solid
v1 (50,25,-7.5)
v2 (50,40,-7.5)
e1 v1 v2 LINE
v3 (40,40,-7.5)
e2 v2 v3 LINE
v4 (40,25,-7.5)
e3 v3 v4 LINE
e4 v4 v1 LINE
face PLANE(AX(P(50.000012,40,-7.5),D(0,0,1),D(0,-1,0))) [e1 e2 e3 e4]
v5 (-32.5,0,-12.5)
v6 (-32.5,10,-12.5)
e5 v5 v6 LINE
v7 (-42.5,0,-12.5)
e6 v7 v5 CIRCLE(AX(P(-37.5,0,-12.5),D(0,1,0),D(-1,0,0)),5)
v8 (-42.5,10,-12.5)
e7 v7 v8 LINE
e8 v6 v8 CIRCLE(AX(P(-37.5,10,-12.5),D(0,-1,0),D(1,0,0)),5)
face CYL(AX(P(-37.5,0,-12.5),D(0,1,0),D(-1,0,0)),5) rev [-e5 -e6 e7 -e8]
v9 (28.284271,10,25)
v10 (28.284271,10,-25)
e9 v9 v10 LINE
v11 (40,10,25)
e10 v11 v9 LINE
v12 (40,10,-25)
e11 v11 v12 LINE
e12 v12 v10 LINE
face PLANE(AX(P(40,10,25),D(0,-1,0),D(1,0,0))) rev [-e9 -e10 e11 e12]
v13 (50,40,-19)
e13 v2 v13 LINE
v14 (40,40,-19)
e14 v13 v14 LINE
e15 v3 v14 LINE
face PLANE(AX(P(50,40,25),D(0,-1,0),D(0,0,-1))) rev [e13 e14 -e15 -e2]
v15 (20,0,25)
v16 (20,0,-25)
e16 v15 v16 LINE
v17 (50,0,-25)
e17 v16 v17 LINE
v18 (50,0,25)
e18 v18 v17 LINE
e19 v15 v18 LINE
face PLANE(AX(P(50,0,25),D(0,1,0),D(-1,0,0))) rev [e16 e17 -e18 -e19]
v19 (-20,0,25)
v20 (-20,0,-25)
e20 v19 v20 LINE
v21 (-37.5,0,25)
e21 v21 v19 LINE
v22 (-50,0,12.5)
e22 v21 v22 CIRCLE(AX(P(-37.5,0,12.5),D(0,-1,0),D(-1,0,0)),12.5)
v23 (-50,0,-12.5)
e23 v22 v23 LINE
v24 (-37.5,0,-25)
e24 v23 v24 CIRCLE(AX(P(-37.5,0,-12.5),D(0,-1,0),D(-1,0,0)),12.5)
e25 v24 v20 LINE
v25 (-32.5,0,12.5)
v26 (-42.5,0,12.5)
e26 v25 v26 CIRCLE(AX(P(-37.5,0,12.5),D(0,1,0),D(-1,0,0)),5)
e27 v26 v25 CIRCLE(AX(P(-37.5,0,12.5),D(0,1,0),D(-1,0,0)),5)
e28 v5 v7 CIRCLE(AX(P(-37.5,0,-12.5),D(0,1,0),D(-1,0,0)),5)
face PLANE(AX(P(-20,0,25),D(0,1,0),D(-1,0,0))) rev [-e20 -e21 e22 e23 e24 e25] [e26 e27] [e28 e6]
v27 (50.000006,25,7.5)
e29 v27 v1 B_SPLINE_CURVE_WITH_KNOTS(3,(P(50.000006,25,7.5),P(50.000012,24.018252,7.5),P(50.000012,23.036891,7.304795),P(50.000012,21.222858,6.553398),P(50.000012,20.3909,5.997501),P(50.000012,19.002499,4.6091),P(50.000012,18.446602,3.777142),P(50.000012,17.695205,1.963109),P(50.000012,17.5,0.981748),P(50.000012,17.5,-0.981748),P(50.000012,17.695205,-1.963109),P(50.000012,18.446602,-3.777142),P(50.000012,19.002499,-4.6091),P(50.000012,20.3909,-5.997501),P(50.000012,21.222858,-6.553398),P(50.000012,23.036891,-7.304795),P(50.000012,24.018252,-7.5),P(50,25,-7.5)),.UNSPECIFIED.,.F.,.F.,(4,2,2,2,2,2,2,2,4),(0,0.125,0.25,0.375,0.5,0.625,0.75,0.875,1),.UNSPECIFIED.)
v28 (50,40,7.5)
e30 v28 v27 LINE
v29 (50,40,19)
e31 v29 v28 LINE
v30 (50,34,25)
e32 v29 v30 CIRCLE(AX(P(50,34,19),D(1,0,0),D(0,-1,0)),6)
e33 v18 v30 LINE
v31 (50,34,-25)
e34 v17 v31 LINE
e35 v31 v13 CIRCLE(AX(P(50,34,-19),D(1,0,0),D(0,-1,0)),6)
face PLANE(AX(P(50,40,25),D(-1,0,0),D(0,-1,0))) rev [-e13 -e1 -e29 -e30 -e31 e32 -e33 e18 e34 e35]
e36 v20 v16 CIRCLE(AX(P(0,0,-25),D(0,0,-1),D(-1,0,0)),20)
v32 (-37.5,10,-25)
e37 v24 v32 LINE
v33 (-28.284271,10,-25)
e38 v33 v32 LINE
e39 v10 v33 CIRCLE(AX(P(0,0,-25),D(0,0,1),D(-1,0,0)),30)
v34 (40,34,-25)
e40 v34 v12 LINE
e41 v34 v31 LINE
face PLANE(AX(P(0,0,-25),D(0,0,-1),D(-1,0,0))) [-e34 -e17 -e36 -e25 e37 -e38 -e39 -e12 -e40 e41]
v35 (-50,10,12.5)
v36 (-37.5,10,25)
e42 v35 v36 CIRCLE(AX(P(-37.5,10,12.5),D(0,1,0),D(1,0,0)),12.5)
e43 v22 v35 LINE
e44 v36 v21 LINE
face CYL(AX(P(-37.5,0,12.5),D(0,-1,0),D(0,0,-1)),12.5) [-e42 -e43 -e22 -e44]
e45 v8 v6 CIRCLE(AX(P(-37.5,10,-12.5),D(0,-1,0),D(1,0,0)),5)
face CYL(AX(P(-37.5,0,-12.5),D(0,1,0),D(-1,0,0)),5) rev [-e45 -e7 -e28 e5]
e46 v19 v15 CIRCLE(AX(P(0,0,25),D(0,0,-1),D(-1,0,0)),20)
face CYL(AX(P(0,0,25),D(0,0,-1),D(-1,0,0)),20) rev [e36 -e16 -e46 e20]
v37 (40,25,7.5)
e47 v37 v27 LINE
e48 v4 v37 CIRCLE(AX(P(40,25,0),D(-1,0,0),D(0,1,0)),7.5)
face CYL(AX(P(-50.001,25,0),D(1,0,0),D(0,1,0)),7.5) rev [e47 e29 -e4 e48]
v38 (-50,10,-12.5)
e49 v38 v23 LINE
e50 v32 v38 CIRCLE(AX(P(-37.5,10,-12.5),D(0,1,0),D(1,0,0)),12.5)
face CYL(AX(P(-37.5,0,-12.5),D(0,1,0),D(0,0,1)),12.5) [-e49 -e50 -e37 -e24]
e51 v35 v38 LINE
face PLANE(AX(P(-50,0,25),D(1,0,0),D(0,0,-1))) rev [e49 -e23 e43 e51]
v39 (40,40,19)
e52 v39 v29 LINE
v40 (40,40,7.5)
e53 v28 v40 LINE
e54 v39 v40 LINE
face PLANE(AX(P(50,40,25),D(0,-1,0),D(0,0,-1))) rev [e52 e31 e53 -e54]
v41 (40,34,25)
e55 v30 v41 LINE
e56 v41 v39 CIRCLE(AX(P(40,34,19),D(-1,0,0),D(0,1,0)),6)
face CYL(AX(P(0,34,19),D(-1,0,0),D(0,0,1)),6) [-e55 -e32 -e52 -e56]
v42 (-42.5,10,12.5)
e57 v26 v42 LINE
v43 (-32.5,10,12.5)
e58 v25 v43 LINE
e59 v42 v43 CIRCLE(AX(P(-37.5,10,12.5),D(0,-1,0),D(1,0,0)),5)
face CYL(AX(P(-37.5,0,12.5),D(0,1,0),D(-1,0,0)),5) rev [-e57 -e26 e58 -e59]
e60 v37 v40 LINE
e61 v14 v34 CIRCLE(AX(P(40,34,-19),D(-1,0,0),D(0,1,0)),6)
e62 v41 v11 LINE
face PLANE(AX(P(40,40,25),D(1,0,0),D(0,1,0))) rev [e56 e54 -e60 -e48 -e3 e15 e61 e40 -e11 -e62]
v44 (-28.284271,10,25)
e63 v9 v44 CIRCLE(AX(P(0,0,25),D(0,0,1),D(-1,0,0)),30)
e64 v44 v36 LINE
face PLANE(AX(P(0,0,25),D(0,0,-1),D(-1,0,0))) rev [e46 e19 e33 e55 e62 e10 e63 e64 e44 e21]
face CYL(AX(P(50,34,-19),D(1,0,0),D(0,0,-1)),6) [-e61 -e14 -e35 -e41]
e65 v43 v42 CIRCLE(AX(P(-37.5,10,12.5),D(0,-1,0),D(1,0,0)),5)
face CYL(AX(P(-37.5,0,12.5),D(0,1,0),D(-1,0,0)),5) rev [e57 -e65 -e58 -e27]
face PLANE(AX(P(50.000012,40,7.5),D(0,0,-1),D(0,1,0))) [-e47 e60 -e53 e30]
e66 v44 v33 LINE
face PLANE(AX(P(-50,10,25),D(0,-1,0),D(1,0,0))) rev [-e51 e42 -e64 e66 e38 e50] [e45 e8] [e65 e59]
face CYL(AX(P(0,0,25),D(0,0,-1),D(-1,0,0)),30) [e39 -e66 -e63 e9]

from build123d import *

# Parameters (mm, degrees)
BASE_BODY_EXTRUDE_DEPTH         = 25
FLANGE_END_ROUNDS_R12_5_R       = 12.5
EDGE_FILLETS_R6_R               = 6
FLANGE_BOLT_HOLES_2X_DEPTH      = 64.442887702
FLANGE_BOLT_HOLES_2X_DEPTH_BACK = 64.442887702
FLANGE_HOLES_SKETCH_R           = 5
FORK_SLOT_REACH                 = 112.567
FORK_SLOT_DIRECTION_2_DEPTH     = 111.566721937


with BuildPart() as part:
    # Base Profile Sketch → Base Body Extrude (new, symmetric)
    with BuildSketch(Plane.XY):
        with BuildLine():
            Line((50, 40), (50, 0))
            Line((50, 0), (20, 0))
            ThreePointArc((20, 0), (0, 20), (-20, 0))
            Line((-20, 0), (-50, 0))
            Line((-50, 0), (-50, 10))
            Line((-50, 10), (-28.284271247, 10))
            ThreePointArc((-28.284271247, 10), (0, 30), (28.284271247, 10))
            Line((28.284271247, 10), (40, 10))
            Line((40, 10), (40, 40))
            Line((40, 40), (50, 40))
        make_face()
    extrude(amount=BASE_BODY_EXTRUDE_DEPTH, both=True)

    # Flange End Rounds R12.5
    flange_end_rounds_r12_5_edges = [part.edges().sort_by_distance(p)[0] for p in [
        (-50, 5, 25),
        (-50, 5, -25),
    ]]
    fillet(flange_end_rounds_r12_5_edges, radius=FLANGE_END_ROUNDS_R12_5_R)

    # Edge Fillets R6
    edge_fillets_r6_edges = [part.edges().sort_by_distance(p)[0] for p in [
        (45, 40, -25),
        (45, 40, 25),
    ]]
    fillet(edge_fillets_r6_edges, radius=EDGE_FILLETS_R6_R)

    # Flange Holes Sketch → Flange Bolt Holes 2x (cut, two sides: drawn at the far end of the back side and taken through both)
    with BuildSketch(Plane(origin=(0, 10, 0), x_dir=(1, 0, 0), z_dir=(0, 1, 0)).offset(-FLANGE_BOLT_HOLES_2X_DEPTH_BACK)):
        with Locations(Location((-37.5, -12.5, 0), (0, 0, 180))):
            Circle(FLANGE_HOLES_SKETCH_R)
        with Locations(Location((-37.5, 12.5, 0), (0, 0, 180))):
            Circle(FLANGE_HOLES_SKETCH_R)
    extrude(amount=FLANGE_BOLT_HOLES_2X_DEPTH + FLANGE_BOLT_HOLES_2X_DEPTH_BACK, mode=Mode.SUBTRACT)

    # Fork Slot Sketch → Fork Slot (cut, up to next)
    with BuildSketch(Plane(origin=(50, 0, 0), x_dir=(0, 0, -1), z_dir=(1, 0, 0)), mode=Mode.PRIVATE) as fork_slot_sk1:
        with BuildLine():
            Line((7.5, 40), (7.5, 25))
            ThreePointArc((7.5, 25), (0, 17.5), (-7.5, 25))
            Line((-7.5, 25), (-7.5, 40))
            Line((-7.5, 40), (7.5, 40))
        make_face()
    fork_slot_tool1 = extrude(fork_slot_sk1.sketch, amount=-FORK_SLOT_REACH, mode=Mode.PRIVATE) & part.part
    add(fork_slot_tool1.solids().sort_by_distance((50, 29.487689, 0))[0], mode=Mode.SUBTRACT)

    # Fork Slot Sketch → Fork Slot direction 2 (cut)
    with BuildSketch(Plane(origin=(50, 0, 0), x_dir=(0, 0, -1), z_dir=(1, 0, 0))):
        with BuildLine():
            Line((7.5, 40), (7.5, 25))
            ThreePointArc((7.5, 25), (0, 17.5), (-7.5, 25))
            Line((-7.5, 25), (-7.5, 40))
            Line((-7.5, 40), (7.5, 40))
        make_face()
    extrude(amount=FORK_SLOT_DIRECTION_2_DEPTH, mode=Mode.SUBTRACT)


solid = part.part
